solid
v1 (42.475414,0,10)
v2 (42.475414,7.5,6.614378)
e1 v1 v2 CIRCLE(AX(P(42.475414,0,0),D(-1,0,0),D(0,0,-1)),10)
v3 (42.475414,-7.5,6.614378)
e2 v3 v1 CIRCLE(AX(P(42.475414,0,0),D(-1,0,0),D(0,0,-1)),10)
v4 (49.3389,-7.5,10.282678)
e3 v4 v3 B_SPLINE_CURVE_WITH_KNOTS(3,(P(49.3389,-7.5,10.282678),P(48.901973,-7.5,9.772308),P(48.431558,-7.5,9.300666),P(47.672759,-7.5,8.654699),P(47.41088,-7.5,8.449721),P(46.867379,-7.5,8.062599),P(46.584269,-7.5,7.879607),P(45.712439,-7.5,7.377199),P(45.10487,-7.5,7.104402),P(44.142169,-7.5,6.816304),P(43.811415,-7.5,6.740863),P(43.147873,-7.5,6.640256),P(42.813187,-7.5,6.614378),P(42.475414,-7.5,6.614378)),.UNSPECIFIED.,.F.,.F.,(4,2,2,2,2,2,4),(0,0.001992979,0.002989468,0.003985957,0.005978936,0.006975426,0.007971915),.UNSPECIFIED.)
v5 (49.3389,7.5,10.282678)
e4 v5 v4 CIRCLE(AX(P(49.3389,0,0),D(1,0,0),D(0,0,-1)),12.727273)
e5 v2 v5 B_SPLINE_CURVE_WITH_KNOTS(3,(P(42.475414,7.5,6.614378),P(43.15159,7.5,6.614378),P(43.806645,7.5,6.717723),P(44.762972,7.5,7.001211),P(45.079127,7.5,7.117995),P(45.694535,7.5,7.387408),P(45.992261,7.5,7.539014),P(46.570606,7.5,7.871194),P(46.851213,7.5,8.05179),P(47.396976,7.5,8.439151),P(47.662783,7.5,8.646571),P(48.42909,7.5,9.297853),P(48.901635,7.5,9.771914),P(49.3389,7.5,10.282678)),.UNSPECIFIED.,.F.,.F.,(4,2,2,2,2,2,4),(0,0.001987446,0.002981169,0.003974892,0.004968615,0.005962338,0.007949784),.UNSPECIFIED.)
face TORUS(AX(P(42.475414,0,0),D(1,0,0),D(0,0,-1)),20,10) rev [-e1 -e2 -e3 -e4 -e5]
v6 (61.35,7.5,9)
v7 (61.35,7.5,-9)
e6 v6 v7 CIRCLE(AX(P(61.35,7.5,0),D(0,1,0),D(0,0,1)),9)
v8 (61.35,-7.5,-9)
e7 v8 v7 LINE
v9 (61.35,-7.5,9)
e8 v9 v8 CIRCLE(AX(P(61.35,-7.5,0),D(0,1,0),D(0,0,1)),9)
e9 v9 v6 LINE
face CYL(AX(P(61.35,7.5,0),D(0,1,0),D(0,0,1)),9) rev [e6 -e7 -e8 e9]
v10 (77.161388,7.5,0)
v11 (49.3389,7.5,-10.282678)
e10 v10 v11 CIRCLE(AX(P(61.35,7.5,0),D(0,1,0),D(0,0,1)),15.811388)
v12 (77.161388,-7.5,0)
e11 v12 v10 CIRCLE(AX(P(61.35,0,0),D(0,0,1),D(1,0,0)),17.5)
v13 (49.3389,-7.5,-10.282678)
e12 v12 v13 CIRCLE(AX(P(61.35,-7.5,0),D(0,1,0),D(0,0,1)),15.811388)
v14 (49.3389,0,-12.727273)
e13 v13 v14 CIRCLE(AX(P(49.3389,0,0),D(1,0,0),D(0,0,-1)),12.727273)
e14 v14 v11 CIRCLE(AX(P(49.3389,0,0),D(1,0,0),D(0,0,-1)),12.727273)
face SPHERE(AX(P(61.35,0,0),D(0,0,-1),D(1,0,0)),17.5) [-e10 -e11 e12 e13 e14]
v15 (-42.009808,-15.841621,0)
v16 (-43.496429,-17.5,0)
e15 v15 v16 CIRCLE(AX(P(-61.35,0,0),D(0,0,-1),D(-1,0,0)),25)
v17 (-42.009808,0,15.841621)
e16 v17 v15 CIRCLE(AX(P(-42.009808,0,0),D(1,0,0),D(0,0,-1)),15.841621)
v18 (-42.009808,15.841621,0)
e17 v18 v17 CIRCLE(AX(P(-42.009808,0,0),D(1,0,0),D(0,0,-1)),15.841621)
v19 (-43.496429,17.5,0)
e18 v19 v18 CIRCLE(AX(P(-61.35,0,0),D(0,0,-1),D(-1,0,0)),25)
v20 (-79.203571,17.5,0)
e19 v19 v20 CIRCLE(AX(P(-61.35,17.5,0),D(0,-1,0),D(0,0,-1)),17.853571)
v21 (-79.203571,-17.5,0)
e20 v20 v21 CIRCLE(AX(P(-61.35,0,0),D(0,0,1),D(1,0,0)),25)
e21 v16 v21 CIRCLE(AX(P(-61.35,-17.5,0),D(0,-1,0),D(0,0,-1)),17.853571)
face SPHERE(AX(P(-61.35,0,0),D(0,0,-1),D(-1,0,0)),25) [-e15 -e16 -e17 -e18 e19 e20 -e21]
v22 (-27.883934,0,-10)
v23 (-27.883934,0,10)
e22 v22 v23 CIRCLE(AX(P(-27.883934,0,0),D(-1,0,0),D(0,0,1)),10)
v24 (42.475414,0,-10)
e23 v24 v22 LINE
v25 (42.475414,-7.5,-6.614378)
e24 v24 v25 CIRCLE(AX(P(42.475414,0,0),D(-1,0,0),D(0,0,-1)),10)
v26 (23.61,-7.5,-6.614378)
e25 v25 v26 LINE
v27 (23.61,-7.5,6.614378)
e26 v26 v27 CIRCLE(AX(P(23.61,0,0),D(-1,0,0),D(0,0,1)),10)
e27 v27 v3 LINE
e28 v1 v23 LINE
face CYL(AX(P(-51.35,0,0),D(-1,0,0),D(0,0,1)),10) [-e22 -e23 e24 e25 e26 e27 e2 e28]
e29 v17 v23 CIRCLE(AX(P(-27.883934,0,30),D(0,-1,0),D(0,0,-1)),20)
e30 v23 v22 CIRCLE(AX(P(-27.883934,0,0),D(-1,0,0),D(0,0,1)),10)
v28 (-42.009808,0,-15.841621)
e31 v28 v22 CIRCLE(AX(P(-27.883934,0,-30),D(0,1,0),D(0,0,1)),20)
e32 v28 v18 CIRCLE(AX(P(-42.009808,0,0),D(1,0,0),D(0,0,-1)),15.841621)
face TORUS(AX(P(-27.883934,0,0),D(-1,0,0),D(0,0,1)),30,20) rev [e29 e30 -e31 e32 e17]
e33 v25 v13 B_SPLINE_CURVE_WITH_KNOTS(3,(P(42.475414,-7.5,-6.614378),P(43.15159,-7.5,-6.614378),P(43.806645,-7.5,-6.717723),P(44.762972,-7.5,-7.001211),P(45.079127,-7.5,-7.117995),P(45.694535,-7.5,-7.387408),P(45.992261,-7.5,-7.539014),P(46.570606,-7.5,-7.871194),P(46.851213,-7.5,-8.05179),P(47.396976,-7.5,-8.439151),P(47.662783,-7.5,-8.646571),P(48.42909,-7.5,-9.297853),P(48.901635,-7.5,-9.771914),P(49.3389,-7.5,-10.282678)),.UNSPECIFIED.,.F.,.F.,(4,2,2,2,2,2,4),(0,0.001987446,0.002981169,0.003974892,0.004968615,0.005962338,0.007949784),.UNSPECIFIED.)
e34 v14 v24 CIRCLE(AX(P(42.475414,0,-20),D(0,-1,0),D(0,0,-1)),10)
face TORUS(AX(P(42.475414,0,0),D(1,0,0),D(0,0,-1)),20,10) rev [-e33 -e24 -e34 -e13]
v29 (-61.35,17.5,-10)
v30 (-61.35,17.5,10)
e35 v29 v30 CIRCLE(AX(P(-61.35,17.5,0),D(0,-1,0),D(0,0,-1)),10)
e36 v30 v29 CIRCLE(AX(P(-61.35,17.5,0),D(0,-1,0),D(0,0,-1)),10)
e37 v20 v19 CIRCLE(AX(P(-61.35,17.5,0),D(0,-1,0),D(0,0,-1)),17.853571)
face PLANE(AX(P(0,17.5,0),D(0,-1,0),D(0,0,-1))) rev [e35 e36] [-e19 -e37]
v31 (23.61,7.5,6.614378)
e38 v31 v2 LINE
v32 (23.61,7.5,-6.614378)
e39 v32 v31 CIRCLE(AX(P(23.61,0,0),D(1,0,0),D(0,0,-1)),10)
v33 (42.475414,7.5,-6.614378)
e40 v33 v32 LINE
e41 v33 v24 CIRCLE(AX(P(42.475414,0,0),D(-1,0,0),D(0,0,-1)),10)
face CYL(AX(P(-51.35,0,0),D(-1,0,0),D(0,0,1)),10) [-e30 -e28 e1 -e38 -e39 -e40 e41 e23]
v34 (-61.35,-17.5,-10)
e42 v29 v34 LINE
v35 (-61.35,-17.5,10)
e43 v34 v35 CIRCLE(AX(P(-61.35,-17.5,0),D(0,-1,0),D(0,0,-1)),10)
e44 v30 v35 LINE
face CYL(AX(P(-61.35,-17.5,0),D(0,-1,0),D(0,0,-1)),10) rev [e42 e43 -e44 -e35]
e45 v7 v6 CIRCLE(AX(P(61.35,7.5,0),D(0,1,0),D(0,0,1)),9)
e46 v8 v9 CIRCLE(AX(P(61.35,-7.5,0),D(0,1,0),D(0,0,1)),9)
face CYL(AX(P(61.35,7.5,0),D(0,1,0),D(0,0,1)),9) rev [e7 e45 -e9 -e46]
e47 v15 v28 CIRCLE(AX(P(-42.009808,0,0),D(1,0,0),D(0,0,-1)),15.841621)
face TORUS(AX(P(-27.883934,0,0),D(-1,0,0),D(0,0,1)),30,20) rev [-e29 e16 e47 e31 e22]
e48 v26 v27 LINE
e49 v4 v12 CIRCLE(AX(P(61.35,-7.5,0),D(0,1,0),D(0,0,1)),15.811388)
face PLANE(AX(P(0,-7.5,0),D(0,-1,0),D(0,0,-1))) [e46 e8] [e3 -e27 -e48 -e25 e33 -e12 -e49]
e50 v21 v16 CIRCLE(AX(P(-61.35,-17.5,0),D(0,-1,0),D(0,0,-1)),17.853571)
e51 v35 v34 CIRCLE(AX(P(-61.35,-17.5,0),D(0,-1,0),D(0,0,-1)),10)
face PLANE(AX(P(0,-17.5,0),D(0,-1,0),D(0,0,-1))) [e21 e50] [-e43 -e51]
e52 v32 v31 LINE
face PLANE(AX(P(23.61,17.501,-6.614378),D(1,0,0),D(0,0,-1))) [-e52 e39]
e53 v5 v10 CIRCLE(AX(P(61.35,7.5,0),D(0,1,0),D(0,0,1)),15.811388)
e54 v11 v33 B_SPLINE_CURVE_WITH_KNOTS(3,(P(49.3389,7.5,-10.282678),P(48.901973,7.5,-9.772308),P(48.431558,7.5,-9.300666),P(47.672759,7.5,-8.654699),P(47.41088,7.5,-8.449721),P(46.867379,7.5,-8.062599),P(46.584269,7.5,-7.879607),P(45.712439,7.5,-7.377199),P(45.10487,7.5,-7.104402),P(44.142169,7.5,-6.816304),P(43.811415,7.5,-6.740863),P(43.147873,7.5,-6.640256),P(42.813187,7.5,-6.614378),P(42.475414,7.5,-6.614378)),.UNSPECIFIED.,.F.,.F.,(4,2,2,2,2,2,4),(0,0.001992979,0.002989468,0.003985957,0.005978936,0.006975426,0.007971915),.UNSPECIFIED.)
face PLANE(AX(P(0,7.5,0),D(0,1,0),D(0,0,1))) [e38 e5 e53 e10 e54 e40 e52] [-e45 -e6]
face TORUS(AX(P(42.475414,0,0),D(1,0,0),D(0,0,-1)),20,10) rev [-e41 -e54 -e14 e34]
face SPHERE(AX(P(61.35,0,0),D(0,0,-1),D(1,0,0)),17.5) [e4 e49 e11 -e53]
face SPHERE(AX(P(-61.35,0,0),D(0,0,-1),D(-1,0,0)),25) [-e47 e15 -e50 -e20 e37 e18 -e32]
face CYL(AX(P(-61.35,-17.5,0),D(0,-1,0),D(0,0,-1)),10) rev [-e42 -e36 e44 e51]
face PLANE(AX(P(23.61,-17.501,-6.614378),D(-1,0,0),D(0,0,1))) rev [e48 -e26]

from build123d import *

# Parameters (mm, degrees)
END_BLEND_FILLET_R10_A_R = 10
END_BLEND_FILLET_R10_B_R = 10
SHAFT_FLAT_CUT_REACH     = 101.084
SHAFT_START              = 7.5
SHAFT_FLAT_SKETCH_W      = 28.74
SHAFT_FLAT_SKETCH_H      = 13.228756556


with BuildPart() as part:
    # Rod Revolve Profile → Rod Body Revolve (revolve)
    with BuildSketch(Plane.XY, mode=Mode.PRIVATE) as rod_body_revolve_sk:
        with BuildLine():
            ThreePointArc((-43.496428929, 17.5), (-36.54418797, 11.972243623), (-27.883933933, 10))
            Line((-27.883933933, 10), (52.35, 10))
            Line((52.35, 10), (52.35, 0))
            Line((52.35, 0), (-51.35, 0))
            Line((-51.35, 0), (-51.35, 17.5))
            Line((-51.35, 17.5), (-43.496428929, 17.5))
        make_face()
    revolve(rod_body_revolve_sk.sketch.rotate(Axis((-51.35, 0, 0), (1, 0, 0)), 90), axis=Axis((-51.35, 0, 0), (1, 0, 0)))

    # Sketch5_17 → End Boss Revolve A (revolve)
    with BuildSketch(Plane.XY, mode=Mode.PRIVATE) as end_boss_revolve_a_sk:
        with BuildLine():
            Line((-71.35, 17.5), (-79.203571071, 17.5))
            ThreePointArc((-79.203571071, 17.5), (-86.35, 0), (-79.203571071, -17.5))
            Line((-79.203571071, -17.5), (-71.35, -17.5))
            Line((-71.35, -17.5), (-71.35, 17.5))
        make_face()
    revolve(end_boss_revolve_a_sk.sketch.rotate(Axis((-61.35, -17.5, 0), (0, 1, 0)), 270), axis=Axis((-61.35, -17.5, 0), (0, 1, 0)))

    # Sketch5_18 → End Boss Revolve B (revolve)
    with BuildSketch(Plane.XY, mode=Mode.PRIVATE) as end_boss_revolve_b_sk:
        with BuildLine():
            Line((77.161388301, -7.5), (70.35, -7.5))
            Line((70.35, -7.5), (70.35, 7.5))
            Line((70.35, 7.5), (77.161388301, 7.5))
            ThreePointArc((77.161388301, 7.5), (78.85, 0), (77.161388301, -7.5))
        make_face()
    revolve(end_boss_revolve_b_sk.sketch.rotate(Axis((61.35, 7.5, 0), (0, -1, 0)), 180), axis=Axis((61.35, 7.5, 0), (0, -1, 0)))

    # End Blend Fillet R10 A
    end_blend_fillet_r10_a_edges = [part.edges().sort_by_distance(p)[0] for p in [
        (46.988593384, 4.114378278, 9.114378278),
    ]]
    fillet(end_blend_fillet_r10_a_edges, radius=END_BLEND_FILLET_R10_A_R)

    # End Blend Fillet R10 B
    end_blend_fillet_r10_b_edges = [part.edges().sort_by_distance(p)[0] for p in [
        (46.988593384, 0, -10),
    ]]
    fillet(end_blend_fillet_r10_b_edges, radius=END_BLEND_FILLET_R10_B_R)

    # Shaft Flat Sketch → Shaft Flat Cut (cut, up to next)
    with BuildSketch(Plane(origin=(0, 0, 0), x_dir=(1, 0, 0), z_dir=(0, 1, 0)).offset(SHAFT_START), mode=Mode.PRIVATE) as shaft_flat_cut_sk1:
        with Locations((37.98, 0)):
            Rectangle(SHAFT_FLAT_SKETCH_W, SHAFT_FLAT_SKETCH_H)
    shaft_flat_cut_tool1 = extrude(shaft_flat_cut_sk1.sketch, amount=SHAFT_FLAT_CUT_REACH, mode=Mode.PRIVATE) & part.part
    shaft_flat_cut = shaft_flat_cut_tool1.solids().sort_by_distance((37.98, 7.5, 0))[0]
    add(shaft_flat_cut, mode=Mode.SUBTRACT)

    # Shaft Flat Mirror: Shaft Flat Cut across plane
    add(shaft_flat_cut.mirror(Plane.ZX), mode=Mode.SUBTRACT)


solid = part.part
